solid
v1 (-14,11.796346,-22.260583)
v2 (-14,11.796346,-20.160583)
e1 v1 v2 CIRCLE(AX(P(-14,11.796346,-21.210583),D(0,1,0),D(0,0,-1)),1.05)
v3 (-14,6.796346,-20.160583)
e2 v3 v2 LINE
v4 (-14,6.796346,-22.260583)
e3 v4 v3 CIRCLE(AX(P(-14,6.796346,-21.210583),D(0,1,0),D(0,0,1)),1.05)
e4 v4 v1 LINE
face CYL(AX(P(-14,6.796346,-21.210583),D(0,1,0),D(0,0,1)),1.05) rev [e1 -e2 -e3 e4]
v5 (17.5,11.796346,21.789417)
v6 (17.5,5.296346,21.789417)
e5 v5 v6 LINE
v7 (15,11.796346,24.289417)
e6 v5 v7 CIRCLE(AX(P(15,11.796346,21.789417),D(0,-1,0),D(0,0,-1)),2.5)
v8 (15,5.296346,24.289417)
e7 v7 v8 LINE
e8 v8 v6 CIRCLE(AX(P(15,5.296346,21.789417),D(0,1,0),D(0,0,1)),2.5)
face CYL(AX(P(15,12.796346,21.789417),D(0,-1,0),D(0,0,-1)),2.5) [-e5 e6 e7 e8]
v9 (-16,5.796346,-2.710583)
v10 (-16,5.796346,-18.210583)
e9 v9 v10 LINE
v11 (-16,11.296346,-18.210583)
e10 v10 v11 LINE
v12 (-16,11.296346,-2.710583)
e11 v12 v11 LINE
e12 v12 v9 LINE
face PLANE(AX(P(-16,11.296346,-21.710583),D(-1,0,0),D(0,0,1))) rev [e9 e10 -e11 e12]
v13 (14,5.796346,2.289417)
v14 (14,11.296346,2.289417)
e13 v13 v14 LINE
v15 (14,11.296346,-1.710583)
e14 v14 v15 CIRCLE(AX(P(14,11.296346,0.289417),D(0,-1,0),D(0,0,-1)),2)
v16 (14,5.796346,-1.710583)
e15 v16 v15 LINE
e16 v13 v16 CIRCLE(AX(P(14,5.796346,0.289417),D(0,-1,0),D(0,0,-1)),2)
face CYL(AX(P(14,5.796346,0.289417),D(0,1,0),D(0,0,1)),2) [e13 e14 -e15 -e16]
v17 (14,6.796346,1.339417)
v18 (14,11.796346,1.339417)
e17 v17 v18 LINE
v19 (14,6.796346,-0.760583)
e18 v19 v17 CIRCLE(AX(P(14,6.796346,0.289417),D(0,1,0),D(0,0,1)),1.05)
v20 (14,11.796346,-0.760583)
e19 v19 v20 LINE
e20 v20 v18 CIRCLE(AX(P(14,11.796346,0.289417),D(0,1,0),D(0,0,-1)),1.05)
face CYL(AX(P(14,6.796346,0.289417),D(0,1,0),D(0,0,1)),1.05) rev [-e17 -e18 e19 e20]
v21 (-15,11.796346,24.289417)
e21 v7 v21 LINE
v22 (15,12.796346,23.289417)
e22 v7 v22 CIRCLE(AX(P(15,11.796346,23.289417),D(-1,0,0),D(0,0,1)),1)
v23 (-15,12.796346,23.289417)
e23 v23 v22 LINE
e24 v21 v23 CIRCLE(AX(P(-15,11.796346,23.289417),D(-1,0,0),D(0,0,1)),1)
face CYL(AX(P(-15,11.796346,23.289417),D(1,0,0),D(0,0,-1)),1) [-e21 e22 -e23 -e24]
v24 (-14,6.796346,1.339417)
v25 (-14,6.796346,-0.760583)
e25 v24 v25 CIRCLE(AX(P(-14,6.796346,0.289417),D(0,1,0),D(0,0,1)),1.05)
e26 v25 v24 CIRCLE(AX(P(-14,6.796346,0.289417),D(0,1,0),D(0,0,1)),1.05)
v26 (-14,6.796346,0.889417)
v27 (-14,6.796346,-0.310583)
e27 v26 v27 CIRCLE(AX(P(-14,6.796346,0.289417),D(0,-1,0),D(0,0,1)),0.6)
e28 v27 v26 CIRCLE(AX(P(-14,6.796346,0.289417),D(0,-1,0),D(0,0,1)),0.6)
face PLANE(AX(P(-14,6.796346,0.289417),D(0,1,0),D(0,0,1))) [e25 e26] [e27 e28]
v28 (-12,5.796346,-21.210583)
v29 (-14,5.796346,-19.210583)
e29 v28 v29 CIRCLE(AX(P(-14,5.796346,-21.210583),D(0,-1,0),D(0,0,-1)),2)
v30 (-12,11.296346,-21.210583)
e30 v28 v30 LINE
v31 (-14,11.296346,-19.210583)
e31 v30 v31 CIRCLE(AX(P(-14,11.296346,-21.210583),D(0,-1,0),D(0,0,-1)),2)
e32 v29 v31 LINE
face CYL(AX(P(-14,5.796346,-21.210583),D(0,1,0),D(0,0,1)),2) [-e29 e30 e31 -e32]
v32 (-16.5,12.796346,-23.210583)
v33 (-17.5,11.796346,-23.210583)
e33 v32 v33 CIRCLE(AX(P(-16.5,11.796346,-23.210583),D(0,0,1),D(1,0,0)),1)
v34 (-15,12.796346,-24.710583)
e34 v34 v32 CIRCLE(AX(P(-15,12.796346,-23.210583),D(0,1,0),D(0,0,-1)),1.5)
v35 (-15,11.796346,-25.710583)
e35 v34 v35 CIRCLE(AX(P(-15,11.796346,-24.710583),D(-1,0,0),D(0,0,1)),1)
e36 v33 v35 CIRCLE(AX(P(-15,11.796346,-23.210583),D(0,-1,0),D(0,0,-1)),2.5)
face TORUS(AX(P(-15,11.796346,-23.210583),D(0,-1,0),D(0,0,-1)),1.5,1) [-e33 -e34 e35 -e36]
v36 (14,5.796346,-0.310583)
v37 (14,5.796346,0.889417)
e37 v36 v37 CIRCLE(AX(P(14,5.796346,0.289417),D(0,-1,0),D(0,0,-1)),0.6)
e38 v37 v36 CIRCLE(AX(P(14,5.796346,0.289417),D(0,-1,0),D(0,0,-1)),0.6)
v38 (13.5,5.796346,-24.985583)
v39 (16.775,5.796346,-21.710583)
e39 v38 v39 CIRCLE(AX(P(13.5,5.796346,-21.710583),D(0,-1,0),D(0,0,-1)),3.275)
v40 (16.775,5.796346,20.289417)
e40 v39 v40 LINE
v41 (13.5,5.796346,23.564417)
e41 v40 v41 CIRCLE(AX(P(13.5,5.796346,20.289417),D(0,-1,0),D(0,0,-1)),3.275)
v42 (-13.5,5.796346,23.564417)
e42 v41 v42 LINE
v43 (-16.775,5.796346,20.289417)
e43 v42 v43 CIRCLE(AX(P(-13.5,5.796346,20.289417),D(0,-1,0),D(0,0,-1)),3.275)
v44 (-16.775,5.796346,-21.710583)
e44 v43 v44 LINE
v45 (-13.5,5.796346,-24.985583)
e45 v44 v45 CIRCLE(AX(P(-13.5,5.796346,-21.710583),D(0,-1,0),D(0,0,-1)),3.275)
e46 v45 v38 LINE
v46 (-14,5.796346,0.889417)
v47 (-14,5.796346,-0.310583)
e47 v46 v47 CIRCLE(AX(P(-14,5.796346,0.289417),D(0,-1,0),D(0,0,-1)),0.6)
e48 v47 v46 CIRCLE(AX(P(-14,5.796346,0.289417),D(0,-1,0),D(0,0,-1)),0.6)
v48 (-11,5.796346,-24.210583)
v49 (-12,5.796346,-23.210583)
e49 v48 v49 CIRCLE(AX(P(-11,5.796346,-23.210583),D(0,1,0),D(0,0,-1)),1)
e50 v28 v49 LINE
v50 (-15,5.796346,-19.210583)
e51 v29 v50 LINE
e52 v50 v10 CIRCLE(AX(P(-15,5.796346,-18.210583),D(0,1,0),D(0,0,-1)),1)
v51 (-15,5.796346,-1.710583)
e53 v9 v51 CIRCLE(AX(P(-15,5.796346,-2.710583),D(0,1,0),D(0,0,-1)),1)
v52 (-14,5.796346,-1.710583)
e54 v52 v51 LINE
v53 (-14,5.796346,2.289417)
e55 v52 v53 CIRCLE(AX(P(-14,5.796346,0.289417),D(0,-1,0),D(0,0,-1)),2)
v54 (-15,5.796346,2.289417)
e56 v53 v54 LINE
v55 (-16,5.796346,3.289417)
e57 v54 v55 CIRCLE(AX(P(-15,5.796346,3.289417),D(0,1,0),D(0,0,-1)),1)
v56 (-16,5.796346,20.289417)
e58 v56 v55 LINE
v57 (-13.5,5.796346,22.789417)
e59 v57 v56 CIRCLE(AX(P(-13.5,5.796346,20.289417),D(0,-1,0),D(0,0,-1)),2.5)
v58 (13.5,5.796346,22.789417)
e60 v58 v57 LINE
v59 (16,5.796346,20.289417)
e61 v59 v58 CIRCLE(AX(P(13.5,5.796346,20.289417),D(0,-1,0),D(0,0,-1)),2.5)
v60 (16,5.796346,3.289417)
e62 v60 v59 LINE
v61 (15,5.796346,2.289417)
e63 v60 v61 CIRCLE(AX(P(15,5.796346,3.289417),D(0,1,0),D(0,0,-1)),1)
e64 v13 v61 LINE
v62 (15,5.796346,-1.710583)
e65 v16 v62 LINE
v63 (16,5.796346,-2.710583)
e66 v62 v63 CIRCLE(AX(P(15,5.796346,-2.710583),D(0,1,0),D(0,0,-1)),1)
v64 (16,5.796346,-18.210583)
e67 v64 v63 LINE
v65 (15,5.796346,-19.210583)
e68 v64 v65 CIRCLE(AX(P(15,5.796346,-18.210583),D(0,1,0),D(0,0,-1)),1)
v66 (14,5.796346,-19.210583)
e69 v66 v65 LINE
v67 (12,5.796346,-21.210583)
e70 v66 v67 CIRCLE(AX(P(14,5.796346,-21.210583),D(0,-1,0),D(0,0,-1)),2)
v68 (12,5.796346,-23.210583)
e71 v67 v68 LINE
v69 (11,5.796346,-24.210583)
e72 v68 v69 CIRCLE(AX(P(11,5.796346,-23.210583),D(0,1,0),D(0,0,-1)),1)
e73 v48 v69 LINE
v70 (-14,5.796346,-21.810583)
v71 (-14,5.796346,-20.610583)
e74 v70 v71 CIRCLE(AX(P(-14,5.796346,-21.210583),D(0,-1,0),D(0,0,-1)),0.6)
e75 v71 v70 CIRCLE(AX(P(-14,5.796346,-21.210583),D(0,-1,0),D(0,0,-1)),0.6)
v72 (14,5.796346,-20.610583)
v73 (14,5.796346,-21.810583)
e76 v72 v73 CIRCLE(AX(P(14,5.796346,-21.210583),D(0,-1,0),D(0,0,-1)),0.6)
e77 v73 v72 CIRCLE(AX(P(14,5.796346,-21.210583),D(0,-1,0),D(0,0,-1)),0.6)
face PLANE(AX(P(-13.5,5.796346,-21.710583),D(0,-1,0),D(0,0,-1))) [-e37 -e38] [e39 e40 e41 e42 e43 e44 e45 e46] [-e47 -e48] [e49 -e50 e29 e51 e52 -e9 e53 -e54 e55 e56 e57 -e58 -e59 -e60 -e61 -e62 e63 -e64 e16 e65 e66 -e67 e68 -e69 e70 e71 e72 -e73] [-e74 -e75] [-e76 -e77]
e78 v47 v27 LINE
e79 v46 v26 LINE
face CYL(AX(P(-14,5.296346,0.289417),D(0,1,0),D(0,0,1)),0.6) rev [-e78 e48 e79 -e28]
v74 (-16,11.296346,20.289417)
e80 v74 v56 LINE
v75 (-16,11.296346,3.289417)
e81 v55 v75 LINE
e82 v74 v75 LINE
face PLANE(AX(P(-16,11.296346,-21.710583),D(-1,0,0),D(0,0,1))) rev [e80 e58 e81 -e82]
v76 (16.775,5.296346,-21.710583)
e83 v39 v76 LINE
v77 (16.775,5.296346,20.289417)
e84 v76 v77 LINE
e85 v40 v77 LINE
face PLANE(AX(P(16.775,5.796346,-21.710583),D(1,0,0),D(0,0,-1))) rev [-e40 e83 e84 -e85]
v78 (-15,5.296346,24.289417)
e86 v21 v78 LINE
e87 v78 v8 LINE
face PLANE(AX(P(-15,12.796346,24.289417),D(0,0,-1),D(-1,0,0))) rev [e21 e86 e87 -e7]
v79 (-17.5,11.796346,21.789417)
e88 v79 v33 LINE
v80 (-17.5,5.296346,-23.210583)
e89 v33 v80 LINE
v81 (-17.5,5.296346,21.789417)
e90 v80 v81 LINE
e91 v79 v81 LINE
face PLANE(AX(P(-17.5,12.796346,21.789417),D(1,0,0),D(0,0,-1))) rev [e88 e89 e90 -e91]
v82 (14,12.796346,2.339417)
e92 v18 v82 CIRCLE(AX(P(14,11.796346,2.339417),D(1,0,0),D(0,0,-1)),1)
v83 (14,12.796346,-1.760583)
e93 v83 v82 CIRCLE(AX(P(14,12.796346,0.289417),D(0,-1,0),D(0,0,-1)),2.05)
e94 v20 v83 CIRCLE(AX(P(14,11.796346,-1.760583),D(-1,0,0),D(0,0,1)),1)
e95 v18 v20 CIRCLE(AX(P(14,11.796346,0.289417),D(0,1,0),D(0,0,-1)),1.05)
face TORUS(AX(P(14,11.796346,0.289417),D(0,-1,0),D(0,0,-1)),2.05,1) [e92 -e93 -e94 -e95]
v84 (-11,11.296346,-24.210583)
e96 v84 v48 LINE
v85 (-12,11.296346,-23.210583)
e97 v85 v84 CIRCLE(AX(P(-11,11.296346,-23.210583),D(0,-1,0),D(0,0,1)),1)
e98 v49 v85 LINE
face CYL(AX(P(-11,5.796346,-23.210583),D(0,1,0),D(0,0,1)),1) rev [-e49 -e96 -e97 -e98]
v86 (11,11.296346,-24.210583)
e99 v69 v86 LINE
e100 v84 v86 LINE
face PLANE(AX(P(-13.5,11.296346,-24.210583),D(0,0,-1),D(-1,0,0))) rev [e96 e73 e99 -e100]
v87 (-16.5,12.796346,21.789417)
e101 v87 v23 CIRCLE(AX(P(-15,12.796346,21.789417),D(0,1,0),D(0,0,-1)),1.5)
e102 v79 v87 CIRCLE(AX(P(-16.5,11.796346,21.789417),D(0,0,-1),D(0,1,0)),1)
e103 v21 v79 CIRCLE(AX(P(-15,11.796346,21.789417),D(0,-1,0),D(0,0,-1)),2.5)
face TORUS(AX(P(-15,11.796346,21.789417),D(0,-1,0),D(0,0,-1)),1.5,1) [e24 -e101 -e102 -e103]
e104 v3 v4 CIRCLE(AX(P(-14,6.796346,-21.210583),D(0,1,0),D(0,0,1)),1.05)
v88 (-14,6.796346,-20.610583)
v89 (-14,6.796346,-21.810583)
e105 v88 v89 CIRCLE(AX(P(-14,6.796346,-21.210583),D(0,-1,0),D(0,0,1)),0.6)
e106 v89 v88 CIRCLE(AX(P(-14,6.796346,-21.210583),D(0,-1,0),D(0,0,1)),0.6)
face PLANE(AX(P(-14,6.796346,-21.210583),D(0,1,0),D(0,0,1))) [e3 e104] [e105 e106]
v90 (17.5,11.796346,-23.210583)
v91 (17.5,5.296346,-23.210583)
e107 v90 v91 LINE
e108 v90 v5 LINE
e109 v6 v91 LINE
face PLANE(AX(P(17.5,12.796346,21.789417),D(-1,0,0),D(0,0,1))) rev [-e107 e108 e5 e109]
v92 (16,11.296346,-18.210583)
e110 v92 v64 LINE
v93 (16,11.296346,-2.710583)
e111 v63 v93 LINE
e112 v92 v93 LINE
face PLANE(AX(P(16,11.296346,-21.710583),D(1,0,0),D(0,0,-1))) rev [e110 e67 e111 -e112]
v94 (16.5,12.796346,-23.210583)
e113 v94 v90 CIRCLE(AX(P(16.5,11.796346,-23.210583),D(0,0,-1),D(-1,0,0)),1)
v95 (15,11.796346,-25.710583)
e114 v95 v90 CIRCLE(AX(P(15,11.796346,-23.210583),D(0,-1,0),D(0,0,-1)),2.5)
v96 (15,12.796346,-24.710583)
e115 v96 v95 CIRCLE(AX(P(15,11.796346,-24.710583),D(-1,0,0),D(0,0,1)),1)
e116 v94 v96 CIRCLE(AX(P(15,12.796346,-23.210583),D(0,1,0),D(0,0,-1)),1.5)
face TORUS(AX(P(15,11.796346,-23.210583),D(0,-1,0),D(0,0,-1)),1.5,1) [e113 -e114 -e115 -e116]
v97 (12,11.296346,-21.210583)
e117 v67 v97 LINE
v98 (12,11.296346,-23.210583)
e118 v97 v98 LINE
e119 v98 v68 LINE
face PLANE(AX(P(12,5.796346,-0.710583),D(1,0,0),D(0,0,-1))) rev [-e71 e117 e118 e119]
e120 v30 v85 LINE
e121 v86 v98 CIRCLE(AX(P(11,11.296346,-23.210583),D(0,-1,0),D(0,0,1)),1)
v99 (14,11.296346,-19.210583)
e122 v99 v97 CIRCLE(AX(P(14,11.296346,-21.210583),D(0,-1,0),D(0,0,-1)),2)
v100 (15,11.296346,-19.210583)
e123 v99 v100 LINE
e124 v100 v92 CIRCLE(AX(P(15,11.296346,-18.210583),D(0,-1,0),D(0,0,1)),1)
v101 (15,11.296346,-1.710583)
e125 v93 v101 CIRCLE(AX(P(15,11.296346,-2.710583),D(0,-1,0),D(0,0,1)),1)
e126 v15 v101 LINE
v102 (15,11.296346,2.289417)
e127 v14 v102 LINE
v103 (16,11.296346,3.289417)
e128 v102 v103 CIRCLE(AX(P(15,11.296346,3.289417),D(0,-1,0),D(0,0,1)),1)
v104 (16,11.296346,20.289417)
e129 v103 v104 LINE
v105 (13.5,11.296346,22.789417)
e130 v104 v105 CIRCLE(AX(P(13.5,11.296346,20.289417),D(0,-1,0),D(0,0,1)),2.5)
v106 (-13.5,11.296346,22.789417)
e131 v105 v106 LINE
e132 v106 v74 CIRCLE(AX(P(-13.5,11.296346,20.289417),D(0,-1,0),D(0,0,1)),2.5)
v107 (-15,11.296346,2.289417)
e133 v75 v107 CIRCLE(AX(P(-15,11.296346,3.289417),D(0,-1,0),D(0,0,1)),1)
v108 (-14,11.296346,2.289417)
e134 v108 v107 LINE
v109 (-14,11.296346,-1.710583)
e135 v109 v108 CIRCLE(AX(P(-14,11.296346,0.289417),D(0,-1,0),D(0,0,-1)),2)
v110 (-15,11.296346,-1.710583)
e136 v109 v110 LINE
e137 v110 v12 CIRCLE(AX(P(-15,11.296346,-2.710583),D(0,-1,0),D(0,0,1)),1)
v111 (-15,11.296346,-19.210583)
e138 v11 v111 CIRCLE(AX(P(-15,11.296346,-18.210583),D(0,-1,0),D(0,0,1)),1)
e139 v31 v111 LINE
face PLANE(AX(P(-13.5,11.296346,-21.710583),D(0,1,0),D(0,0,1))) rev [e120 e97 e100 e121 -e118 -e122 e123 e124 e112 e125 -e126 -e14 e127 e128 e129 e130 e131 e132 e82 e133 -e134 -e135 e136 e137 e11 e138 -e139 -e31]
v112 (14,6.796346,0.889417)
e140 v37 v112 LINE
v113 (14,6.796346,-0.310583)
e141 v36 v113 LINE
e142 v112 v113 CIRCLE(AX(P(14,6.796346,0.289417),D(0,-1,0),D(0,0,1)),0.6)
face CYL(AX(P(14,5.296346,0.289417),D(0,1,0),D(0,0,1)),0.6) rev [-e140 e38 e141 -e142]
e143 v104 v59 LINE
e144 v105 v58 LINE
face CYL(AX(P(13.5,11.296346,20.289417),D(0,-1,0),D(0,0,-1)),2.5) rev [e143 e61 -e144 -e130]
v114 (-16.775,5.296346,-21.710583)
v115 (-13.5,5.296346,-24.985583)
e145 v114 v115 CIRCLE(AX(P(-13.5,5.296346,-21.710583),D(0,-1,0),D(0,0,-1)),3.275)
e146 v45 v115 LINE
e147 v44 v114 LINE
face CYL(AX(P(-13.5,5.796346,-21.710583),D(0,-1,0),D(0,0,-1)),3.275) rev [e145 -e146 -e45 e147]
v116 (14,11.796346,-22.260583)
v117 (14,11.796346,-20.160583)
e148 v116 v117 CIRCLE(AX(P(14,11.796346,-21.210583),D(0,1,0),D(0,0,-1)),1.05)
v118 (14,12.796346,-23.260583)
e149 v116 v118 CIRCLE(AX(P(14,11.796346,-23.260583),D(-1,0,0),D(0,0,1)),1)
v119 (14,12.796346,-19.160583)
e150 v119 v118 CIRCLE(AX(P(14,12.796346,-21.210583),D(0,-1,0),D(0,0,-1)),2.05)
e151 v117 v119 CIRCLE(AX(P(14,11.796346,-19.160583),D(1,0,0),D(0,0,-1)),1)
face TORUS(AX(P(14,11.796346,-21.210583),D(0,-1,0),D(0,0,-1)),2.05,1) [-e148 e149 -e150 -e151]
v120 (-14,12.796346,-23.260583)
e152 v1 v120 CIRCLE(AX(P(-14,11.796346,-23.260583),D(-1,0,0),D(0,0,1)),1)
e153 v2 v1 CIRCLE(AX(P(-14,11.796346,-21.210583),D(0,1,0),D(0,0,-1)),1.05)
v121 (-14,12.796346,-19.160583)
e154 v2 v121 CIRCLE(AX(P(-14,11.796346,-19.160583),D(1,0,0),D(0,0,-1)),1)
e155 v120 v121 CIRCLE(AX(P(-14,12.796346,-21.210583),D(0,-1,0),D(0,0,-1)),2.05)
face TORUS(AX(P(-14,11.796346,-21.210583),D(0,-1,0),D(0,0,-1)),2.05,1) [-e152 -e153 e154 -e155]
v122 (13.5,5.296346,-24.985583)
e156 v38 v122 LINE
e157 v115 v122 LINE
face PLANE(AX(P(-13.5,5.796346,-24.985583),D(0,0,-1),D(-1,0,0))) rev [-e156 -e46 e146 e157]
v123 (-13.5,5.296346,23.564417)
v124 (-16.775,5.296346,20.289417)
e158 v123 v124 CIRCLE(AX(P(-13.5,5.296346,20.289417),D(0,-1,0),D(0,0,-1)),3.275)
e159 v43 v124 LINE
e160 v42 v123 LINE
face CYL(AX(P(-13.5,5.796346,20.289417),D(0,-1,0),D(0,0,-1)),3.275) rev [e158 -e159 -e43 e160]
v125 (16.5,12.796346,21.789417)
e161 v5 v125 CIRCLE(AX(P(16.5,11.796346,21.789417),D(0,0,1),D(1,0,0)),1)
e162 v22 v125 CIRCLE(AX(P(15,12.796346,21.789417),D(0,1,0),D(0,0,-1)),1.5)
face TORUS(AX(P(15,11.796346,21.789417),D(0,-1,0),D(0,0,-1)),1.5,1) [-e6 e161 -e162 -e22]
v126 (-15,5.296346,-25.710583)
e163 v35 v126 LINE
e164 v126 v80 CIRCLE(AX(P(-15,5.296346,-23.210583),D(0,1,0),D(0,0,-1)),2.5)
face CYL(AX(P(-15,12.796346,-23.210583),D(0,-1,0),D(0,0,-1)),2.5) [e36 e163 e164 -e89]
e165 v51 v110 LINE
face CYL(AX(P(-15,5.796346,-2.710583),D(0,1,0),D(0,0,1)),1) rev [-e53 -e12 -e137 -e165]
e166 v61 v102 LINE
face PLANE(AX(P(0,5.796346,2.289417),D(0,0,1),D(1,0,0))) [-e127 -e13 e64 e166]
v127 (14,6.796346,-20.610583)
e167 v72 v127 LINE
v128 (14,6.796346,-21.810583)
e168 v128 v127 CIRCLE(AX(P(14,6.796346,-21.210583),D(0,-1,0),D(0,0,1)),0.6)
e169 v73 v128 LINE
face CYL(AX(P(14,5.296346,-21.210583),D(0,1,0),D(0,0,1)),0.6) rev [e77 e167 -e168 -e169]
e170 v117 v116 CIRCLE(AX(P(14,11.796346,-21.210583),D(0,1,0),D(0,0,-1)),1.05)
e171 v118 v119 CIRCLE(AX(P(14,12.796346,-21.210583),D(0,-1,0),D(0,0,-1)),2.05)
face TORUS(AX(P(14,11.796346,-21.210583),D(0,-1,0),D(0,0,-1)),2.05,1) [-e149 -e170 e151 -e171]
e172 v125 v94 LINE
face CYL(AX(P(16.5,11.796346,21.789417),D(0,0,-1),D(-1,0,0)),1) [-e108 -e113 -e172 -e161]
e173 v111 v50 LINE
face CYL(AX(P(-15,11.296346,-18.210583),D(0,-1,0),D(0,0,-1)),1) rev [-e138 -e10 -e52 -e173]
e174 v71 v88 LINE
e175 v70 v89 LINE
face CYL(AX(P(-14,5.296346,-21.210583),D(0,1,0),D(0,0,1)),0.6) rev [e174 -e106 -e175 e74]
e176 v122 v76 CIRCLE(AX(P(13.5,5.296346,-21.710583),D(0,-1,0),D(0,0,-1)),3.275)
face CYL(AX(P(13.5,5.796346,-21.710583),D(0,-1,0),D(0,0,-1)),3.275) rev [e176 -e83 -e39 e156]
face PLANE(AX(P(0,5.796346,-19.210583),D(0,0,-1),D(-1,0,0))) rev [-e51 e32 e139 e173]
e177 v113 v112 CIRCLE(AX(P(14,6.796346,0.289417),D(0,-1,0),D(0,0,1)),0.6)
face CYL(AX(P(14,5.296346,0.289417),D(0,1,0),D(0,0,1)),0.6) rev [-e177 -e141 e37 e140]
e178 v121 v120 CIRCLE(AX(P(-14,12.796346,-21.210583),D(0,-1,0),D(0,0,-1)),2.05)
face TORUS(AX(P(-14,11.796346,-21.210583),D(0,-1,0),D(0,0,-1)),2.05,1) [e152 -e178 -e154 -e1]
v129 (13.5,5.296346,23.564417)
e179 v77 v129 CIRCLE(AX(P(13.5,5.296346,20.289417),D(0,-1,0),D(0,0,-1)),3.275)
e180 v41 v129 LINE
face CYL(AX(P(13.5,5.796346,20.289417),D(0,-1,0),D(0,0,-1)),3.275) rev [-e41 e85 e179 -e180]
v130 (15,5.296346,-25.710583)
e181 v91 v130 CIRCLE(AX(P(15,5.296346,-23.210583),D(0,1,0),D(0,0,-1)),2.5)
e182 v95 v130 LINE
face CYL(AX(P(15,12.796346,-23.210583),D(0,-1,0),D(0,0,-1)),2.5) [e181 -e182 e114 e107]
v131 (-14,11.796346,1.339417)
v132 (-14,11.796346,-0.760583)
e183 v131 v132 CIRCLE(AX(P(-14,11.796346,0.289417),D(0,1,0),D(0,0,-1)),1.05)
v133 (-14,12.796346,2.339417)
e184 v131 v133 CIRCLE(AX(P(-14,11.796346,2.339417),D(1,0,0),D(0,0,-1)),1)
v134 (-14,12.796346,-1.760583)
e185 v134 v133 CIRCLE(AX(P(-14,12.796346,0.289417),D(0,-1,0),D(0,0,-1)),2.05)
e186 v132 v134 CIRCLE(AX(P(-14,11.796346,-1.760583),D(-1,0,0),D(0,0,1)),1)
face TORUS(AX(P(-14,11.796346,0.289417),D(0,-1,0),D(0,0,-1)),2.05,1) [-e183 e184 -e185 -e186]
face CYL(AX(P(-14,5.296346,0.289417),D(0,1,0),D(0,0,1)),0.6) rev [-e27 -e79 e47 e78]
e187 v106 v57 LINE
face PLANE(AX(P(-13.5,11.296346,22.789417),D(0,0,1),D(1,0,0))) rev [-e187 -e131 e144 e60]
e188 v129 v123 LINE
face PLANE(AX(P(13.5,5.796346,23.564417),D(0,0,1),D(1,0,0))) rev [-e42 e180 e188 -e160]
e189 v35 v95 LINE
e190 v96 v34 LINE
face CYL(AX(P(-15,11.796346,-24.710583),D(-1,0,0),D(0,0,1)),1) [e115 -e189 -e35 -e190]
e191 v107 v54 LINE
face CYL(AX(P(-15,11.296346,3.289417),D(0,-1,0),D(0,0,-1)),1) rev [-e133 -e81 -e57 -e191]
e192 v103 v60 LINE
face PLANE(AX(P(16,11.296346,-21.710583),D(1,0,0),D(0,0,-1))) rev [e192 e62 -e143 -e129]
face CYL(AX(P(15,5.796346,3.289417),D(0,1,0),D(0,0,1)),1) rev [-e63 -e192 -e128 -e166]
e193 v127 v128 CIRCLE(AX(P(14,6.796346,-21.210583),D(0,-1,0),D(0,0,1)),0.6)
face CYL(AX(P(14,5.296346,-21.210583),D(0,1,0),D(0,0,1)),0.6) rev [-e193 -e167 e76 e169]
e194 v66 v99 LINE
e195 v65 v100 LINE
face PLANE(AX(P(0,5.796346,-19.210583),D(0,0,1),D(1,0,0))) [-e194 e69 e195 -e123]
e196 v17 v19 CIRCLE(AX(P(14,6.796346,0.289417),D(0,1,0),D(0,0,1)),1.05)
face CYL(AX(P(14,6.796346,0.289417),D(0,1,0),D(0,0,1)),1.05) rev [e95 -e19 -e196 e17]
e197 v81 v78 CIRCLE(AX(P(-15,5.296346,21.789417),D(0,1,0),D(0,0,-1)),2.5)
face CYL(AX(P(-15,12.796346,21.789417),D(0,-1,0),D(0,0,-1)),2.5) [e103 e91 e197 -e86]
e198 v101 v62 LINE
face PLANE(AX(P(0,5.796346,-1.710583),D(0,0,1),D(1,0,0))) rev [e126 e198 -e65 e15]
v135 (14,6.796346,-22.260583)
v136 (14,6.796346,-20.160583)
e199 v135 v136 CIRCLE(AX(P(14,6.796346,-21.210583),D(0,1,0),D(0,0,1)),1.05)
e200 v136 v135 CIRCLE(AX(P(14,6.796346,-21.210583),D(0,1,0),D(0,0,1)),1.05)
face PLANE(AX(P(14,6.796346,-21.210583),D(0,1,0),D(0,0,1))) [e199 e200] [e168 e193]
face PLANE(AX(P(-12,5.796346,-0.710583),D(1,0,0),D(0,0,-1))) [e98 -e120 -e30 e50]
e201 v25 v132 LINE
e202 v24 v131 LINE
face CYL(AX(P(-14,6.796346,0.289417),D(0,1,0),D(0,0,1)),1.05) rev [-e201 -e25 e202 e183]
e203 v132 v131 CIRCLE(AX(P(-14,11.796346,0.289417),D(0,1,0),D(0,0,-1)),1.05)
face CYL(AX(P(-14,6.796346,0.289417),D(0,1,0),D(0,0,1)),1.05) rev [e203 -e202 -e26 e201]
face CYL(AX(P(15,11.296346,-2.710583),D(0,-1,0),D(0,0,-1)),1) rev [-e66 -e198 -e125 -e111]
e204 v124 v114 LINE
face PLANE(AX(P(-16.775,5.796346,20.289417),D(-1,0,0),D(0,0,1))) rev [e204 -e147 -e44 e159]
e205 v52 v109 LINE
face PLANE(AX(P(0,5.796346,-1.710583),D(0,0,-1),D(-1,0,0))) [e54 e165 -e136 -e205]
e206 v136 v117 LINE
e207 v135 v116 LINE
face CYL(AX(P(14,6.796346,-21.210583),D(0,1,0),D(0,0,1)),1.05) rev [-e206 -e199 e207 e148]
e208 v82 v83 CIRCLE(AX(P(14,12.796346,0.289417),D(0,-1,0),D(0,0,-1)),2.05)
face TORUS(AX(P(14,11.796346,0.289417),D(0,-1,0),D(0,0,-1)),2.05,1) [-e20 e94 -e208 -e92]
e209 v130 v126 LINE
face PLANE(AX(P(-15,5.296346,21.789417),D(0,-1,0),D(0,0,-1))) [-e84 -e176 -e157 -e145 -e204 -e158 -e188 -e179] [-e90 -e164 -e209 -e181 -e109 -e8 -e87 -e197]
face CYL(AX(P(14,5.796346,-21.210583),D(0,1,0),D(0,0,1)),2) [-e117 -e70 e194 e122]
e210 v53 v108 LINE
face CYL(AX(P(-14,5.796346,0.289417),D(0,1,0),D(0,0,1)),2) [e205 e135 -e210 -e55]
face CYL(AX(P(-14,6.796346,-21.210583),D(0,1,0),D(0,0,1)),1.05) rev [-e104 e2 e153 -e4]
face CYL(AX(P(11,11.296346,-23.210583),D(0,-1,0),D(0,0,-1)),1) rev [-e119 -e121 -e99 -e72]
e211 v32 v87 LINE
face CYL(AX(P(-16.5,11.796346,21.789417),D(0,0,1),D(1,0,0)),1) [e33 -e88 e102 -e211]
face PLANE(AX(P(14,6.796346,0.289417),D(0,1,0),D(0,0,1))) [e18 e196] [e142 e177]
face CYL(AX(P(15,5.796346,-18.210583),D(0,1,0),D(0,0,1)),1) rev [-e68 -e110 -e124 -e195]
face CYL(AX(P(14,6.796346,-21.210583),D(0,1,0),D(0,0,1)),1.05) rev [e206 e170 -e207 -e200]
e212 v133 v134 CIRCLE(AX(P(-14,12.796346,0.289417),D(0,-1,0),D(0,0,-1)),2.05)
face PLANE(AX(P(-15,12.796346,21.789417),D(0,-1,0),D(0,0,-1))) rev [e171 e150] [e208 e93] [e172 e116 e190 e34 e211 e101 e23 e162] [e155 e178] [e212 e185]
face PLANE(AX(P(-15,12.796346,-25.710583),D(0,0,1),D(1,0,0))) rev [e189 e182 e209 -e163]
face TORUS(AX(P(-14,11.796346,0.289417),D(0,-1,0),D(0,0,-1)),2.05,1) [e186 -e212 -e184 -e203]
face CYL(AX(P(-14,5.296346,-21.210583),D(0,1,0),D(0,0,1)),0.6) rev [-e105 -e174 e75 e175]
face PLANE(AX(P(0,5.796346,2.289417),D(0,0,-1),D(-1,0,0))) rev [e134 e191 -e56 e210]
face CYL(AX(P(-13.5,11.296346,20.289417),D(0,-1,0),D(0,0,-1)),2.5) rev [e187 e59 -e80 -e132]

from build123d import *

# Parameters (mm, degrees)
BOSS_EXTRUDE1_DEPTH = 15
CUT_EXTRUDE1_DEPTH  = 12
CUT_EXTRUDE2_DEPTH  = 1
BOSS_EXTRUDE2_START = 11
BOSS_EXTRUDE2_DEPTH = 11
SKETCH5_R           = 1.2
CUT_EXTRUDE3_DEPTH  = 63.84902545
SKETCH6_R           = 2.1
CUT_EXTRUDE4_DEPTH  = 12
FILLET1_R           = 2
SCALE1_SCALE        = 0.5
FILLET2_R           = 1


with BuildPart() as part:
    # Sketch1 → Boss-Extrude1 (new body)
    with BuildSketch(Plane(origin=(0, 0, 0), x_dir=(1, 0, 0), z_dir=(0, 1, 0))):
        with BuildLine():
            Line((-30, -50), (30, -50))
            ThreePointArc((30, -50), (33.535533906, -48.535533906), (35, -45))
            Line((35, -45), (35, 45))
            ThreePointArc((35, 45), (33.535533906, 48.535533906), (30, 50))
            Line((30, 50), (-30, 50))
            ThreePointArc((-30, 50), (-33.535533906, 48.535533906), (-35, 45))
            Line((-35, 45), (-35, -45))
            ThreePointArc((-35, -45), (-33.535533906, -48.535533906), (-30, -50))
        make_face()
    extrude(amount=BOSS_EXTRUDE1_DEPTH)

    # Sketch2 → Cut-Extrude1 (cut)
    with BuildSketch(Plane.XZ):
        with BuildLine():
            Line((-27, -47), (27, -47))
            ThreePointArc((27, -47), (30.535533906, -45.535533906), (32, -42))
            Line((32, -42), (32, 42))
            ThreePointArc((32, 42), (30.535533906, 45.535533906), (27, 47))
            Line((27, 47), (-27, 47))
            ThreePointArc((-27, 47), (-30.535533906, 45.535533906), (-32, 42))
            Line((-32, 42), (-32, -42))
            ThreePointArc((-32, -42), (-30.535533906, -45.535533906), (-27, -47))
        make_face()
    extrude(amount=-CUT_EXTRUDE1_DEPTH, mode=Mode.SUBTRACT)

    # Sketch3 → Cut-Extrude2 (cut)
    with BuildSketch(Plane.XZ):
        with BuildLine():
            Line((-27, -48.55), (27, -48.55))
            ThreePointArc((27, -48.55), (31.631549417, -46.631549417), (33.55, -42))
            Line((33.55, -42), (33.55, 42))
            ThreePointArc((33.55, 42), (31.631549417, 46.631549417), (27, 48.55))
            Line((27, 48.55), (-27, 48.55))
            ThreePointArc((-27, 48.55), (-31.631549417, 46.631549417), (-33.55, 42))
            Line((-33.55, 42), (-33.55, -42))
            ThreePointArc((-33.55, -42), (-31.631549417, -46.631549417), (-27, -48.55))
        make_face()
        with BuildLine():
            Line((-27, -47), (27, -47))
            ThreePointArc((27, -47), (30.535533906, -45.535533906), (32, -42))
            Line((32, -42), (32, 42))
            ThreePointArc((32, 42), (30.535533906, 45.535533906), (27, 47))
            Line((27, 47), (-27, 47))
            ThreePointArc((-27, 47), (-30.535533906, 45.535533906), (-32, 42))
            Line((-32, 42), (-32, -42))
            ThreePointArc((-32, -42), (-30.535533906, -45.535533906), (-27, -47))
        make_face(mode=Mode.SUBTRACT)
    extrude(amount=-CUT_EXTRUDE2_DEPTH, mode=Mode.SUBTRACT)

    # Sketch4 → Boss-Extrude2 (add)
    with BuildSketch(Plane.XZ.offset(-12).offset(BOSS_EXTRUDE2_START)):
        with BuildLine():
            ThreePointArc((-28, -2), (-24, 2), (-28, 6))
            Line((-28, 6), (-32, 6))
            Line((-32, 6), (-32, -2))
            Line((-32, -2), (-28, -2))
        make_face()
        with BuildLine():
            Line((-28, -37), (-32, -37))
            Line((-32, -37), (-32, -42))
            ThreePointArc((-32, -42), (-30.535533906, -45.535533906), (-27, -47))
            Line((-27, -47), (-24, -47))
            Line((-24, -47), (-24, -41))
            ThreePointArc((-24, -41), (-25.171572875, -38.171572875), (-28, -37))
        make_face()
        with BuildLine():
            Line((32, -2), (32, 6))
            Line((32, 6), (28, 6))
            ThreePointArc((28, 6), (24, 2), (28, -2))
            Line((28, -2), (32, -2))
        make_face()
        with BuildLine():
            Line((24, -41), (24, -47))
            Line((24, -47), (27, -47))
            ThreePointArc((27, -47), (30.535533906, -45.535533906), (32, -42))
            Line((32, -42), (32, -37))
            Line((32, -37), (28, -37))
            ThreePointArc((28, -37), (25.171572875, -38.171572875), (24, -41))
        make_face()
    extrude(amount=-BOSS_EXTRUDE2_DEPTH)

    # Sketch5 → Cut-Extrude3 (cut, through all)
    with BuildSketch(Plane(origin=(0, 15, 0), x_dir=(1, 0, 0), z_dir=(0, 1, 0))):
        with Locations(Location((28, -2, 0), (0, 0, 270))):
            Circle(SKETCH5_R)
        with Locations(Location((28, 41, 0), (0, 0, 270))):
            Circle(SKETCH5_R)
        with Locations(Location((-28, 41, 0), (0, 0, 270))):
            Circle(SKETCH5_R)
        with Locations(Location((-28, -2, 0), (0, 0, 270))):
            Circle(SKETCH5_R)
    extrude(amount=-CUT_EXTRUDE3_DEPTH, mode=Mode.SUBTRACT)

    # Sketch6 → Cut-Extrude4 (cut)
    with BuildSketch(Plane(origin=(0, 15, 0), x_dir=(1, 0, 0), z_dir=(0, 1, 0))):
        with Locations(Location((28, -2, 0), (0, 0, 270))):
            Circle(SKETCH6_R)
        with Locations(Location((-28, -2, 0), (0, 0, 270))):
            Circle(SKETCH6_R)
        with Locations(Location((-28, 41, 0), (0, 0, 270))):
            Circle(SKETCH6_R)
        with Locations(Location((28, 41, 0), (0, 0, 270))):
            Circle(SKETCH6_R)
    extrude(amount=-CUT_EXTRUDE4_DEPTH, mode=Mode.SUBTRACT)

    # Fillet1
    fillet1_edges = [part.edges().sort_by_distance(p)[0] for p in [
        (33.535533906, 15, 48.535533906),
        (35, 15, 0),
        (33.535533906, 15, -48.535533906),
        (0, 15, -50),
        (28, 15, -43.1),
        (-28, 15, -43.1),
        (-28, 15, -0.1),
        (28, 15, -0.1),
        (-33.535533906, 15, -48.535533906),
        (-35, 15, 0),
        (-33.535533906, 15, 48.535533906),
        (0, 15, 50),
    ]]
    fillet(fillet1_edges, radius=FILLET1_R)


with BuildPart() as part_1:
    # Scale1: scaled about (0, 10.592691126, -1.421166574)
    add(part.part.scale(SCALE1_SCALE).moved(Location((0, 5.296345563, -0.710583287))))

    # Fillet2
    fillet2_edges = [part_1.edges().sort_by_distance(p)[0] for p in [
        (-16, 8.546345563, -1.710583287),
        (-16, 8.546345563, 2.289416713),
        (16, 8.546345563, 2.289416713),
        (16, 8.546345563, -1.710583287),
        (16, 8.546345563, -19.210583287),
        (12, 8.546345563, -24.210583287),
        (-12, 8.546345563, -24.210583287),
        (-16, 8.546345563, -19.210583287),
    ]]
    fillet(fillet2_edges, radius=FILLET2_R)


solid = part_1.part
